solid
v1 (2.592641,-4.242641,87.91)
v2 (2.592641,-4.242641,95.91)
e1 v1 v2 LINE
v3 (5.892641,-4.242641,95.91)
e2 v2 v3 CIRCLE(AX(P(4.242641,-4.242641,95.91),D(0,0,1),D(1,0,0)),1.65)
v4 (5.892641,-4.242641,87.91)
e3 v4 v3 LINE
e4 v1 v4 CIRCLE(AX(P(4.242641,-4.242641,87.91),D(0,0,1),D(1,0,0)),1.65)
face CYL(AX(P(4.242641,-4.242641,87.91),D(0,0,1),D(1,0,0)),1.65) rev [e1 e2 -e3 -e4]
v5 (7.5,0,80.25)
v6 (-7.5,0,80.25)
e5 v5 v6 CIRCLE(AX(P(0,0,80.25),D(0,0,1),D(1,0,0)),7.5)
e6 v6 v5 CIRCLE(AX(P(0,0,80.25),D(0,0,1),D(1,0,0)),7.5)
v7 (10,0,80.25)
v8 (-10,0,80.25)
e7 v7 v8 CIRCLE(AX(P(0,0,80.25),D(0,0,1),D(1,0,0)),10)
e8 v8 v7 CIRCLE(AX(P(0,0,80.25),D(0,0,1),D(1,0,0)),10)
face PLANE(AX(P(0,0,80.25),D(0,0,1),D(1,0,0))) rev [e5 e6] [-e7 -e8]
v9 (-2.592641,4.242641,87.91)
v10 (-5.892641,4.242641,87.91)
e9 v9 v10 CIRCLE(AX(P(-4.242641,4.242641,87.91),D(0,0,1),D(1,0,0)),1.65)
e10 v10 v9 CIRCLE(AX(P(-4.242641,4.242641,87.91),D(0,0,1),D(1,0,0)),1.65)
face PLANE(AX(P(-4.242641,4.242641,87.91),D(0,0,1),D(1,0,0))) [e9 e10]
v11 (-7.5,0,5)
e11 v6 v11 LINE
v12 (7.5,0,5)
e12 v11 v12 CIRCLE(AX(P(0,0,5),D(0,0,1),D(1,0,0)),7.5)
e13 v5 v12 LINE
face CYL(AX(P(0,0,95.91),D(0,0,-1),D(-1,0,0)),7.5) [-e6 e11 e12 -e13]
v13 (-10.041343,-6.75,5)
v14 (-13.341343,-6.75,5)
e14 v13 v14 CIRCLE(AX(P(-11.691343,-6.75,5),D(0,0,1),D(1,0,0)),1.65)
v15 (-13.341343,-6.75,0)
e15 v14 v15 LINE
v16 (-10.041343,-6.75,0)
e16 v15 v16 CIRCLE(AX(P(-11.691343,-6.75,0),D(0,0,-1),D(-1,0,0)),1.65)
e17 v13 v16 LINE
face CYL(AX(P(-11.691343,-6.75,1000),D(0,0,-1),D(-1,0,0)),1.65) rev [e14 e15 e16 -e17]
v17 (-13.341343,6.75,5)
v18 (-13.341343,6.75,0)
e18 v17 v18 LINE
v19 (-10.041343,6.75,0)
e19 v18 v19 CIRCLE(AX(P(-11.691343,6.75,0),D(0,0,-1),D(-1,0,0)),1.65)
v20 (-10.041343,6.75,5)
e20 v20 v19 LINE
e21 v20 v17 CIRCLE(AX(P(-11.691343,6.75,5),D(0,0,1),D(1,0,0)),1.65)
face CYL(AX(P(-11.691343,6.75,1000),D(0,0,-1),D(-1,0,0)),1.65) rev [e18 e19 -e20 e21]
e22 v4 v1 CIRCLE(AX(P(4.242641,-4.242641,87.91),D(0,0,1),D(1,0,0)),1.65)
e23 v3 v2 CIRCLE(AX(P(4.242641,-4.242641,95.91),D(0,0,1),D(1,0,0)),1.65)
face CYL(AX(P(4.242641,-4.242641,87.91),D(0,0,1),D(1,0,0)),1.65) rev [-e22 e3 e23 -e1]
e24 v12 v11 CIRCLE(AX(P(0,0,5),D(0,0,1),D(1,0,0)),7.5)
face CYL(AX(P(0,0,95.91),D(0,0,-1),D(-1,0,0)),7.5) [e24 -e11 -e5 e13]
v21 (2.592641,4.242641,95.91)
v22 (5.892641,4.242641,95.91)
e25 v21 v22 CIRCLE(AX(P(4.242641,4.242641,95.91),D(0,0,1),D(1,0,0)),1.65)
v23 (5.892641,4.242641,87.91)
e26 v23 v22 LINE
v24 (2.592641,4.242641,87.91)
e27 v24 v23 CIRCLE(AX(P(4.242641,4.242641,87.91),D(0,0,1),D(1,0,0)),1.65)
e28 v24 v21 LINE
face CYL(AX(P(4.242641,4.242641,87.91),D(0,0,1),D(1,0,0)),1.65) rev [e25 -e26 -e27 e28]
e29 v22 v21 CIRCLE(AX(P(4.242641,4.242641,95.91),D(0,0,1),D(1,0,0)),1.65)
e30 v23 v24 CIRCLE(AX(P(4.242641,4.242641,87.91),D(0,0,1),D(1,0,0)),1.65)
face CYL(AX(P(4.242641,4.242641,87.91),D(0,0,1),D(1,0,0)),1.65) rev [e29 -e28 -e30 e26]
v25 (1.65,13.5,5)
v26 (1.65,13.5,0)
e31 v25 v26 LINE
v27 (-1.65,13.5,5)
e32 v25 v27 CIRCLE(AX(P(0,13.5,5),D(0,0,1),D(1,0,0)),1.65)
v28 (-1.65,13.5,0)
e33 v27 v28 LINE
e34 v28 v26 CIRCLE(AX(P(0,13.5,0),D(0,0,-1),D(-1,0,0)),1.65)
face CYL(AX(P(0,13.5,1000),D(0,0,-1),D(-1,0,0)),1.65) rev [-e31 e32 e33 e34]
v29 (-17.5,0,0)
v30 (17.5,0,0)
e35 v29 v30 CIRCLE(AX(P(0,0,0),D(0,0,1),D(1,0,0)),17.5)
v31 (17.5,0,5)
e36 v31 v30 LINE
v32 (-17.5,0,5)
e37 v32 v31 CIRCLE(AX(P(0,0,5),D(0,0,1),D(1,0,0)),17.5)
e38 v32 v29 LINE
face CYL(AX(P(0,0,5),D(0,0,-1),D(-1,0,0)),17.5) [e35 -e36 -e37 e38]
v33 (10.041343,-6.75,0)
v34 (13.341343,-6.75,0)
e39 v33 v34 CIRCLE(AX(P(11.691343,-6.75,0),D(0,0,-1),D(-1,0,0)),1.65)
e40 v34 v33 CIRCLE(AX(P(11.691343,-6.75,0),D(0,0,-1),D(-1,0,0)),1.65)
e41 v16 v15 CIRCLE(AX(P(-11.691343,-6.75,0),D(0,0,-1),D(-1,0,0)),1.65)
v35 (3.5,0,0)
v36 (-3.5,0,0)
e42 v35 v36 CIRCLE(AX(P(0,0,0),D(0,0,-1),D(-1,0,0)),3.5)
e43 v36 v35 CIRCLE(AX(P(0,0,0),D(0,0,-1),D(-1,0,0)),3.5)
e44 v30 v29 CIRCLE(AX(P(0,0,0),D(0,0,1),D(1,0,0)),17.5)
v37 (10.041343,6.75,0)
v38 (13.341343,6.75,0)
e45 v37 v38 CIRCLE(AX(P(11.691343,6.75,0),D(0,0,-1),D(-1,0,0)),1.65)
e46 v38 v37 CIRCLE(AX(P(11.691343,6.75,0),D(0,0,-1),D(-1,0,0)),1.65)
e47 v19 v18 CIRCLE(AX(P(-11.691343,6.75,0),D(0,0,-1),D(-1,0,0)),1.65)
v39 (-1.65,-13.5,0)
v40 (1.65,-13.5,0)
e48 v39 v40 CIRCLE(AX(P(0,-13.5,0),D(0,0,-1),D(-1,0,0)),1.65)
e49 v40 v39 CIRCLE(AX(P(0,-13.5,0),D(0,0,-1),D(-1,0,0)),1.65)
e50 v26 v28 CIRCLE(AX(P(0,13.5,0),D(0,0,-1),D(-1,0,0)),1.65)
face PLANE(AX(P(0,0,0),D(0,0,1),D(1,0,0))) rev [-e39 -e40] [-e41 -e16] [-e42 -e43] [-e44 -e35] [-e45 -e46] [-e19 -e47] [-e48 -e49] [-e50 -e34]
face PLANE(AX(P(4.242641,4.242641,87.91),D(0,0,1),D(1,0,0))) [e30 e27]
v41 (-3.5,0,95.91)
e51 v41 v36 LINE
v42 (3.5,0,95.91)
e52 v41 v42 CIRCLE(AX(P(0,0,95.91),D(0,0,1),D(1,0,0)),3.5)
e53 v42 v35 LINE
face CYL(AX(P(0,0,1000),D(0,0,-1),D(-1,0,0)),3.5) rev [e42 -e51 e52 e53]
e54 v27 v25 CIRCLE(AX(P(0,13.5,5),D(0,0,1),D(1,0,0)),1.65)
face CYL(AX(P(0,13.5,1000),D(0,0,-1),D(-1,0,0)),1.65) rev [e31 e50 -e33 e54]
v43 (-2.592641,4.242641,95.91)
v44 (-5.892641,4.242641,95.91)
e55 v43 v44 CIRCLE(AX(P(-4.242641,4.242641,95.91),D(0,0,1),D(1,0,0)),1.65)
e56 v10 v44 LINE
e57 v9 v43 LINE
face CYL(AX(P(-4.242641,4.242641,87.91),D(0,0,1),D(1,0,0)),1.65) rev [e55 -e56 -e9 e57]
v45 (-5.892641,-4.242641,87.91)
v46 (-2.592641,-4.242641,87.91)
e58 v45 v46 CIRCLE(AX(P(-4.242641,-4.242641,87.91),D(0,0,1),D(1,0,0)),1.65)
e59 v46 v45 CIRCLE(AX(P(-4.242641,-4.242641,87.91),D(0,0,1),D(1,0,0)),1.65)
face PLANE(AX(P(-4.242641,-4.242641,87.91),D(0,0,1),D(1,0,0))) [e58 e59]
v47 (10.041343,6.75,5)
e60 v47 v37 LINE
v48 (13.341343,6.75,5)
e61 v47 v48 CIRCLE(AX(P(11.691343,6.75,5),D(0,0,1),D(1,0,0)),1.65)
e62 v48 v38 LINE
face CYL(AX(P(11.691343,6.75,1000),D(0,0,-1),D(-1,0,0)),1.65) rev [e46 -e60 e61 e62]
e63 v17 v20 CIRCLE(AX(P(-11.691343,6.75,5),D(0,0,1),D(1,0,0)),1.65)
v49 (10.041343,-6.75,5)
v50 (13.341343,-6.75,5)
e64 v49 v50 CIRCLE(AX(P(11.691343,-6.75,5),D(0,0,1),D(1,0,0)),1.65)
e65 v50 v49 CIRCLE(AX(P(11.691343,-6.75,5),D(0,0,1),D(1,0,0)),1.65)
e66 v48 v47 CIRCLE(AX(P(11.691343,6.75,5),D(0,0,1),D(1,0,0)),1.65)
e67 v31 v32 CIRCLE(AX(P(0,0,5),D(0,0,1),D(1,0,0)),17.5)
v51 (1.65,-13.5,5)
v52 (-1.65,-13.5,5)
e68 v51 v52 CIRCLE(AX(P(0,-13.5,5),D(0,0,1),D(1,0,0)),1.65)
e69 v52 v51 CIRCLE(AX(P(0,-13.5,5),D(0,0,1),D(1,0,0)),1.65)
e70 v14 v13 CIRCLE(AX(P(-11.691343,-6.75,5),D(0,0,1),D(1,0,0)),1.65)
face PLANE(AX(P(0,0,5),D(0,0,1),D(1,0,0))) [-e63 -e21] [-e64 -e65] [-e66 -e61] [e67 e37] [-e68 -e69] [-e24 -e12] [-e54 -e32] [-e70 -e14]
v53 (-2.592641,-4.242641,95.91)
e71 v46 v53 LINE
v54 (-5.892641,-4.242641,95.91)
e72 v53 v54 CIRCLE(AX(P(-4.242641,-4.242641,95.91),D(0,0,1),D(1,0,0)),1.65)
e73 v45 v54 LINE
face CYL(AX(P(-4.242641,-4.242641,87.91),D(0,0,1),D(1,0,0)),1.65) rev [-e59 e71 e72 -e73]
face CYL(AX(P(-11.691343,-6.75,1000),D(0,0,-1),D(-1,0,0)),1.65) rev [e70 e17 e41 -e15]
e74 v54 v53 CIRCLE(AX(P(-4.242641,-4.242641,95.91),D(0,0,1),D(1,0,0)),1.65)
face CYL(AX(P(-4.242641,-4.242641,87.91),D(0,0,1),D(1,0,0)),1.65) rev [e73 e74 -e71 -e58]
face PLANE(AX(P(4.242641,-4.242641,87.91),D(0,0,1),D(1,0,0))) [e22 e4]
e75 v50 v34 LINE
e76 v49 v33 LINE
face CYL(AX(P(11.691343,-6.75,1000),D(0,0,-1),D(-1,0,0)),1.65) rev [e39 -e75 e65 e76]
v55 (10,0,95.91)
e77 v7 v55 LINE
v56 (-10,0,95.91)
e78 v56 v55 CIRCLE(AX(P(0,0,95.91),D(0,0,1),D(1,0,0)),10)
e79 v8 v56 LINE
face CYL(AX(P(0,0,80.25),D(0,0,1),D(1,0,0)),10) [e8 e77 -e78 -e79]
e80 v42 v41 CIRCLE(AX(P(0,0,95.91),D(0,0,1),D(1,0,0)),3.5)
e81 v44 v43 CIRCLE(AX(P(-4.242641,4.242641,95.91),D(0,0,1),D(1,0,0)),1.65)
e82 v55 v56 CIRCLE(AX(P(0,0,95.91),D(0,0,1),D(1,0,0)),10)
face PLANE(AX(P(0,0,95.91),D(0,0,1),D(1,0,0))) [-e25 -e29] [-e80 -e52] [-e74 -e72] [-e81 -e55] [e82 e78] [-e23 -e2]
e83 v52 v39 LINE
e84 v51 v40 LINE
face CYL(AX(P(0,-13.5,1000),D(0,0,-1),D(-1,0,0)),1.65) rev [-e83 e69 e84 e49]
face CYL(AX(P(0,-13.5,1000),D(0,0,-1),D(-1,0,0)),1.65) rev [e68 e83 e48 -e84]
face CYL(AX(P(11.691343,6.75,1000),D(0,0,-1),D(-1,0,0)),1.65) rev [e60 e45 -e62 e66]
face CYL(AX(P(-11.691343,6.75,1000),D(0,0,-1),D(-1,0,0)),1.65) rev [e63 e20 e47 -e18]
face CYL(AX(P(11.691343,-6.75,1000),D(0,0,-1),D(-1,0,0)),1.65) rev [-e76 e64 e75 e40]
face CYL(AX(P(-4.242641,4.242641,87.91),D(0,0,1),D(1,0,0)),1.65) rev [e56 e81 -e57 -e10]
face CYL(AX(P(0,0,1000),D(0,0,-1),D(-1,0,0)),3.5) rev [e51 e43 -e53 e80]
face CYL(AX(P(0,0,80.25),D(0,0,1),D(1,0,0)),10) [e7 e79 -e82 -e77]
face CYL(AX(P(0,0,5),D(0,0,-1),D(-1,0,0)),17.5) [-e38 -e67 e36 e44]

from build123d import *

# Parameters (mm, degrees)
SKETCH_1_R          = 17.5
EXTRUDE_1_DEPTH     = 5
SKETCH_2_R          = 7.5
EXTRUDE_2_DEPTH     = 90.91
SKETCH_3_R          = 1.65
SKETCH_3_R_2        = 3.5
CUT_EXTRUDE_1_DEPTH = 1000
SKETCH_4_R          = 10
SKETCH_4_R_2        = 4
EXTRUDE_3_DEPTH     = 15.66
SKETCH_5_R          = 1.65
CUT_EXTRUDE_2_DEPTH = 8


with BuildPart() as part:
    # 草图1 → 凸台-拉伸1 (new body)
    with BuildSketch(Plane.XY):
        Circle(SKETCH_1_R)
    extrude(amount=EXTRUDE_1_DEPTH)

    # 草图2 → 凸台-拉伸2 (add)
    with BuildSketch(Plane.XY.offset(5)):
        Circle(SKETCH_2_R)
    extrude(amount=EXTRUDE_2_DEPTH)

    # 草图3 → 切除-拉伸1 (cut)
    with BuildSketch(Plane(origin=(0, 0, 0), x_dir=(-1, 0, 0), z_dir=(0, 0, -1))):
        with Locations((0, 13.5)):
            Circle(SKETCH_3_R)
        with Locations((11.691342951, 6.75)):
            Circle(SKETCH_3_R)
        with Locations((11.691342951, -6.75)):
            Circle(SKETCH_3_R)
        with Locations((0, -13.5)):
            Circle(SKETCH_3_R)
        with Locations((-11.691342951, -6.75)):
            Circle(SKETCH_3_R)
        with Locations((-11.691342951, 6.75)):
            Circle(SKETCH_3_R)
        Circle(SKETCH_3_R_2)
    extrude(amount=-CUT_EXTRUDE_1_DEPTH, mode=Mode.SUBTRACT)

    # 草图4 → 凸台-拉伸3 (add)
    with BuildSketch(Plane.XY.offset(95.91)):
        Circle(SKETCH_4_R)
        Circle(SKETCH_4_R_2, mode=Mode.SUBTRACT)
    extrude(amount=-EXTRUDE_3_DEPTH)

    # 草图5 → 切除-拉伸2 (cut)
    with BuildSketch(Plane.XY.offset(95.91)):
        with Locations((-4.242640687, 4.242640687)):
            Circle(SKETCH_5_R)
        with Locations((-4.242640687, -4.242640687)):
            Circle(SKETCH_5_R)
        with Locations((4.242640687, -4.242640687)):
            Circle(SKETCH_5_R)
        with Locations((4.242640687, 4.242640687)):
            Circle(SKETCH_5_R)
    extrude(amount=-CUT_EXTRUDE_2_DEPTH, mode=Mode.SUBTRACT)


solid = part.part
